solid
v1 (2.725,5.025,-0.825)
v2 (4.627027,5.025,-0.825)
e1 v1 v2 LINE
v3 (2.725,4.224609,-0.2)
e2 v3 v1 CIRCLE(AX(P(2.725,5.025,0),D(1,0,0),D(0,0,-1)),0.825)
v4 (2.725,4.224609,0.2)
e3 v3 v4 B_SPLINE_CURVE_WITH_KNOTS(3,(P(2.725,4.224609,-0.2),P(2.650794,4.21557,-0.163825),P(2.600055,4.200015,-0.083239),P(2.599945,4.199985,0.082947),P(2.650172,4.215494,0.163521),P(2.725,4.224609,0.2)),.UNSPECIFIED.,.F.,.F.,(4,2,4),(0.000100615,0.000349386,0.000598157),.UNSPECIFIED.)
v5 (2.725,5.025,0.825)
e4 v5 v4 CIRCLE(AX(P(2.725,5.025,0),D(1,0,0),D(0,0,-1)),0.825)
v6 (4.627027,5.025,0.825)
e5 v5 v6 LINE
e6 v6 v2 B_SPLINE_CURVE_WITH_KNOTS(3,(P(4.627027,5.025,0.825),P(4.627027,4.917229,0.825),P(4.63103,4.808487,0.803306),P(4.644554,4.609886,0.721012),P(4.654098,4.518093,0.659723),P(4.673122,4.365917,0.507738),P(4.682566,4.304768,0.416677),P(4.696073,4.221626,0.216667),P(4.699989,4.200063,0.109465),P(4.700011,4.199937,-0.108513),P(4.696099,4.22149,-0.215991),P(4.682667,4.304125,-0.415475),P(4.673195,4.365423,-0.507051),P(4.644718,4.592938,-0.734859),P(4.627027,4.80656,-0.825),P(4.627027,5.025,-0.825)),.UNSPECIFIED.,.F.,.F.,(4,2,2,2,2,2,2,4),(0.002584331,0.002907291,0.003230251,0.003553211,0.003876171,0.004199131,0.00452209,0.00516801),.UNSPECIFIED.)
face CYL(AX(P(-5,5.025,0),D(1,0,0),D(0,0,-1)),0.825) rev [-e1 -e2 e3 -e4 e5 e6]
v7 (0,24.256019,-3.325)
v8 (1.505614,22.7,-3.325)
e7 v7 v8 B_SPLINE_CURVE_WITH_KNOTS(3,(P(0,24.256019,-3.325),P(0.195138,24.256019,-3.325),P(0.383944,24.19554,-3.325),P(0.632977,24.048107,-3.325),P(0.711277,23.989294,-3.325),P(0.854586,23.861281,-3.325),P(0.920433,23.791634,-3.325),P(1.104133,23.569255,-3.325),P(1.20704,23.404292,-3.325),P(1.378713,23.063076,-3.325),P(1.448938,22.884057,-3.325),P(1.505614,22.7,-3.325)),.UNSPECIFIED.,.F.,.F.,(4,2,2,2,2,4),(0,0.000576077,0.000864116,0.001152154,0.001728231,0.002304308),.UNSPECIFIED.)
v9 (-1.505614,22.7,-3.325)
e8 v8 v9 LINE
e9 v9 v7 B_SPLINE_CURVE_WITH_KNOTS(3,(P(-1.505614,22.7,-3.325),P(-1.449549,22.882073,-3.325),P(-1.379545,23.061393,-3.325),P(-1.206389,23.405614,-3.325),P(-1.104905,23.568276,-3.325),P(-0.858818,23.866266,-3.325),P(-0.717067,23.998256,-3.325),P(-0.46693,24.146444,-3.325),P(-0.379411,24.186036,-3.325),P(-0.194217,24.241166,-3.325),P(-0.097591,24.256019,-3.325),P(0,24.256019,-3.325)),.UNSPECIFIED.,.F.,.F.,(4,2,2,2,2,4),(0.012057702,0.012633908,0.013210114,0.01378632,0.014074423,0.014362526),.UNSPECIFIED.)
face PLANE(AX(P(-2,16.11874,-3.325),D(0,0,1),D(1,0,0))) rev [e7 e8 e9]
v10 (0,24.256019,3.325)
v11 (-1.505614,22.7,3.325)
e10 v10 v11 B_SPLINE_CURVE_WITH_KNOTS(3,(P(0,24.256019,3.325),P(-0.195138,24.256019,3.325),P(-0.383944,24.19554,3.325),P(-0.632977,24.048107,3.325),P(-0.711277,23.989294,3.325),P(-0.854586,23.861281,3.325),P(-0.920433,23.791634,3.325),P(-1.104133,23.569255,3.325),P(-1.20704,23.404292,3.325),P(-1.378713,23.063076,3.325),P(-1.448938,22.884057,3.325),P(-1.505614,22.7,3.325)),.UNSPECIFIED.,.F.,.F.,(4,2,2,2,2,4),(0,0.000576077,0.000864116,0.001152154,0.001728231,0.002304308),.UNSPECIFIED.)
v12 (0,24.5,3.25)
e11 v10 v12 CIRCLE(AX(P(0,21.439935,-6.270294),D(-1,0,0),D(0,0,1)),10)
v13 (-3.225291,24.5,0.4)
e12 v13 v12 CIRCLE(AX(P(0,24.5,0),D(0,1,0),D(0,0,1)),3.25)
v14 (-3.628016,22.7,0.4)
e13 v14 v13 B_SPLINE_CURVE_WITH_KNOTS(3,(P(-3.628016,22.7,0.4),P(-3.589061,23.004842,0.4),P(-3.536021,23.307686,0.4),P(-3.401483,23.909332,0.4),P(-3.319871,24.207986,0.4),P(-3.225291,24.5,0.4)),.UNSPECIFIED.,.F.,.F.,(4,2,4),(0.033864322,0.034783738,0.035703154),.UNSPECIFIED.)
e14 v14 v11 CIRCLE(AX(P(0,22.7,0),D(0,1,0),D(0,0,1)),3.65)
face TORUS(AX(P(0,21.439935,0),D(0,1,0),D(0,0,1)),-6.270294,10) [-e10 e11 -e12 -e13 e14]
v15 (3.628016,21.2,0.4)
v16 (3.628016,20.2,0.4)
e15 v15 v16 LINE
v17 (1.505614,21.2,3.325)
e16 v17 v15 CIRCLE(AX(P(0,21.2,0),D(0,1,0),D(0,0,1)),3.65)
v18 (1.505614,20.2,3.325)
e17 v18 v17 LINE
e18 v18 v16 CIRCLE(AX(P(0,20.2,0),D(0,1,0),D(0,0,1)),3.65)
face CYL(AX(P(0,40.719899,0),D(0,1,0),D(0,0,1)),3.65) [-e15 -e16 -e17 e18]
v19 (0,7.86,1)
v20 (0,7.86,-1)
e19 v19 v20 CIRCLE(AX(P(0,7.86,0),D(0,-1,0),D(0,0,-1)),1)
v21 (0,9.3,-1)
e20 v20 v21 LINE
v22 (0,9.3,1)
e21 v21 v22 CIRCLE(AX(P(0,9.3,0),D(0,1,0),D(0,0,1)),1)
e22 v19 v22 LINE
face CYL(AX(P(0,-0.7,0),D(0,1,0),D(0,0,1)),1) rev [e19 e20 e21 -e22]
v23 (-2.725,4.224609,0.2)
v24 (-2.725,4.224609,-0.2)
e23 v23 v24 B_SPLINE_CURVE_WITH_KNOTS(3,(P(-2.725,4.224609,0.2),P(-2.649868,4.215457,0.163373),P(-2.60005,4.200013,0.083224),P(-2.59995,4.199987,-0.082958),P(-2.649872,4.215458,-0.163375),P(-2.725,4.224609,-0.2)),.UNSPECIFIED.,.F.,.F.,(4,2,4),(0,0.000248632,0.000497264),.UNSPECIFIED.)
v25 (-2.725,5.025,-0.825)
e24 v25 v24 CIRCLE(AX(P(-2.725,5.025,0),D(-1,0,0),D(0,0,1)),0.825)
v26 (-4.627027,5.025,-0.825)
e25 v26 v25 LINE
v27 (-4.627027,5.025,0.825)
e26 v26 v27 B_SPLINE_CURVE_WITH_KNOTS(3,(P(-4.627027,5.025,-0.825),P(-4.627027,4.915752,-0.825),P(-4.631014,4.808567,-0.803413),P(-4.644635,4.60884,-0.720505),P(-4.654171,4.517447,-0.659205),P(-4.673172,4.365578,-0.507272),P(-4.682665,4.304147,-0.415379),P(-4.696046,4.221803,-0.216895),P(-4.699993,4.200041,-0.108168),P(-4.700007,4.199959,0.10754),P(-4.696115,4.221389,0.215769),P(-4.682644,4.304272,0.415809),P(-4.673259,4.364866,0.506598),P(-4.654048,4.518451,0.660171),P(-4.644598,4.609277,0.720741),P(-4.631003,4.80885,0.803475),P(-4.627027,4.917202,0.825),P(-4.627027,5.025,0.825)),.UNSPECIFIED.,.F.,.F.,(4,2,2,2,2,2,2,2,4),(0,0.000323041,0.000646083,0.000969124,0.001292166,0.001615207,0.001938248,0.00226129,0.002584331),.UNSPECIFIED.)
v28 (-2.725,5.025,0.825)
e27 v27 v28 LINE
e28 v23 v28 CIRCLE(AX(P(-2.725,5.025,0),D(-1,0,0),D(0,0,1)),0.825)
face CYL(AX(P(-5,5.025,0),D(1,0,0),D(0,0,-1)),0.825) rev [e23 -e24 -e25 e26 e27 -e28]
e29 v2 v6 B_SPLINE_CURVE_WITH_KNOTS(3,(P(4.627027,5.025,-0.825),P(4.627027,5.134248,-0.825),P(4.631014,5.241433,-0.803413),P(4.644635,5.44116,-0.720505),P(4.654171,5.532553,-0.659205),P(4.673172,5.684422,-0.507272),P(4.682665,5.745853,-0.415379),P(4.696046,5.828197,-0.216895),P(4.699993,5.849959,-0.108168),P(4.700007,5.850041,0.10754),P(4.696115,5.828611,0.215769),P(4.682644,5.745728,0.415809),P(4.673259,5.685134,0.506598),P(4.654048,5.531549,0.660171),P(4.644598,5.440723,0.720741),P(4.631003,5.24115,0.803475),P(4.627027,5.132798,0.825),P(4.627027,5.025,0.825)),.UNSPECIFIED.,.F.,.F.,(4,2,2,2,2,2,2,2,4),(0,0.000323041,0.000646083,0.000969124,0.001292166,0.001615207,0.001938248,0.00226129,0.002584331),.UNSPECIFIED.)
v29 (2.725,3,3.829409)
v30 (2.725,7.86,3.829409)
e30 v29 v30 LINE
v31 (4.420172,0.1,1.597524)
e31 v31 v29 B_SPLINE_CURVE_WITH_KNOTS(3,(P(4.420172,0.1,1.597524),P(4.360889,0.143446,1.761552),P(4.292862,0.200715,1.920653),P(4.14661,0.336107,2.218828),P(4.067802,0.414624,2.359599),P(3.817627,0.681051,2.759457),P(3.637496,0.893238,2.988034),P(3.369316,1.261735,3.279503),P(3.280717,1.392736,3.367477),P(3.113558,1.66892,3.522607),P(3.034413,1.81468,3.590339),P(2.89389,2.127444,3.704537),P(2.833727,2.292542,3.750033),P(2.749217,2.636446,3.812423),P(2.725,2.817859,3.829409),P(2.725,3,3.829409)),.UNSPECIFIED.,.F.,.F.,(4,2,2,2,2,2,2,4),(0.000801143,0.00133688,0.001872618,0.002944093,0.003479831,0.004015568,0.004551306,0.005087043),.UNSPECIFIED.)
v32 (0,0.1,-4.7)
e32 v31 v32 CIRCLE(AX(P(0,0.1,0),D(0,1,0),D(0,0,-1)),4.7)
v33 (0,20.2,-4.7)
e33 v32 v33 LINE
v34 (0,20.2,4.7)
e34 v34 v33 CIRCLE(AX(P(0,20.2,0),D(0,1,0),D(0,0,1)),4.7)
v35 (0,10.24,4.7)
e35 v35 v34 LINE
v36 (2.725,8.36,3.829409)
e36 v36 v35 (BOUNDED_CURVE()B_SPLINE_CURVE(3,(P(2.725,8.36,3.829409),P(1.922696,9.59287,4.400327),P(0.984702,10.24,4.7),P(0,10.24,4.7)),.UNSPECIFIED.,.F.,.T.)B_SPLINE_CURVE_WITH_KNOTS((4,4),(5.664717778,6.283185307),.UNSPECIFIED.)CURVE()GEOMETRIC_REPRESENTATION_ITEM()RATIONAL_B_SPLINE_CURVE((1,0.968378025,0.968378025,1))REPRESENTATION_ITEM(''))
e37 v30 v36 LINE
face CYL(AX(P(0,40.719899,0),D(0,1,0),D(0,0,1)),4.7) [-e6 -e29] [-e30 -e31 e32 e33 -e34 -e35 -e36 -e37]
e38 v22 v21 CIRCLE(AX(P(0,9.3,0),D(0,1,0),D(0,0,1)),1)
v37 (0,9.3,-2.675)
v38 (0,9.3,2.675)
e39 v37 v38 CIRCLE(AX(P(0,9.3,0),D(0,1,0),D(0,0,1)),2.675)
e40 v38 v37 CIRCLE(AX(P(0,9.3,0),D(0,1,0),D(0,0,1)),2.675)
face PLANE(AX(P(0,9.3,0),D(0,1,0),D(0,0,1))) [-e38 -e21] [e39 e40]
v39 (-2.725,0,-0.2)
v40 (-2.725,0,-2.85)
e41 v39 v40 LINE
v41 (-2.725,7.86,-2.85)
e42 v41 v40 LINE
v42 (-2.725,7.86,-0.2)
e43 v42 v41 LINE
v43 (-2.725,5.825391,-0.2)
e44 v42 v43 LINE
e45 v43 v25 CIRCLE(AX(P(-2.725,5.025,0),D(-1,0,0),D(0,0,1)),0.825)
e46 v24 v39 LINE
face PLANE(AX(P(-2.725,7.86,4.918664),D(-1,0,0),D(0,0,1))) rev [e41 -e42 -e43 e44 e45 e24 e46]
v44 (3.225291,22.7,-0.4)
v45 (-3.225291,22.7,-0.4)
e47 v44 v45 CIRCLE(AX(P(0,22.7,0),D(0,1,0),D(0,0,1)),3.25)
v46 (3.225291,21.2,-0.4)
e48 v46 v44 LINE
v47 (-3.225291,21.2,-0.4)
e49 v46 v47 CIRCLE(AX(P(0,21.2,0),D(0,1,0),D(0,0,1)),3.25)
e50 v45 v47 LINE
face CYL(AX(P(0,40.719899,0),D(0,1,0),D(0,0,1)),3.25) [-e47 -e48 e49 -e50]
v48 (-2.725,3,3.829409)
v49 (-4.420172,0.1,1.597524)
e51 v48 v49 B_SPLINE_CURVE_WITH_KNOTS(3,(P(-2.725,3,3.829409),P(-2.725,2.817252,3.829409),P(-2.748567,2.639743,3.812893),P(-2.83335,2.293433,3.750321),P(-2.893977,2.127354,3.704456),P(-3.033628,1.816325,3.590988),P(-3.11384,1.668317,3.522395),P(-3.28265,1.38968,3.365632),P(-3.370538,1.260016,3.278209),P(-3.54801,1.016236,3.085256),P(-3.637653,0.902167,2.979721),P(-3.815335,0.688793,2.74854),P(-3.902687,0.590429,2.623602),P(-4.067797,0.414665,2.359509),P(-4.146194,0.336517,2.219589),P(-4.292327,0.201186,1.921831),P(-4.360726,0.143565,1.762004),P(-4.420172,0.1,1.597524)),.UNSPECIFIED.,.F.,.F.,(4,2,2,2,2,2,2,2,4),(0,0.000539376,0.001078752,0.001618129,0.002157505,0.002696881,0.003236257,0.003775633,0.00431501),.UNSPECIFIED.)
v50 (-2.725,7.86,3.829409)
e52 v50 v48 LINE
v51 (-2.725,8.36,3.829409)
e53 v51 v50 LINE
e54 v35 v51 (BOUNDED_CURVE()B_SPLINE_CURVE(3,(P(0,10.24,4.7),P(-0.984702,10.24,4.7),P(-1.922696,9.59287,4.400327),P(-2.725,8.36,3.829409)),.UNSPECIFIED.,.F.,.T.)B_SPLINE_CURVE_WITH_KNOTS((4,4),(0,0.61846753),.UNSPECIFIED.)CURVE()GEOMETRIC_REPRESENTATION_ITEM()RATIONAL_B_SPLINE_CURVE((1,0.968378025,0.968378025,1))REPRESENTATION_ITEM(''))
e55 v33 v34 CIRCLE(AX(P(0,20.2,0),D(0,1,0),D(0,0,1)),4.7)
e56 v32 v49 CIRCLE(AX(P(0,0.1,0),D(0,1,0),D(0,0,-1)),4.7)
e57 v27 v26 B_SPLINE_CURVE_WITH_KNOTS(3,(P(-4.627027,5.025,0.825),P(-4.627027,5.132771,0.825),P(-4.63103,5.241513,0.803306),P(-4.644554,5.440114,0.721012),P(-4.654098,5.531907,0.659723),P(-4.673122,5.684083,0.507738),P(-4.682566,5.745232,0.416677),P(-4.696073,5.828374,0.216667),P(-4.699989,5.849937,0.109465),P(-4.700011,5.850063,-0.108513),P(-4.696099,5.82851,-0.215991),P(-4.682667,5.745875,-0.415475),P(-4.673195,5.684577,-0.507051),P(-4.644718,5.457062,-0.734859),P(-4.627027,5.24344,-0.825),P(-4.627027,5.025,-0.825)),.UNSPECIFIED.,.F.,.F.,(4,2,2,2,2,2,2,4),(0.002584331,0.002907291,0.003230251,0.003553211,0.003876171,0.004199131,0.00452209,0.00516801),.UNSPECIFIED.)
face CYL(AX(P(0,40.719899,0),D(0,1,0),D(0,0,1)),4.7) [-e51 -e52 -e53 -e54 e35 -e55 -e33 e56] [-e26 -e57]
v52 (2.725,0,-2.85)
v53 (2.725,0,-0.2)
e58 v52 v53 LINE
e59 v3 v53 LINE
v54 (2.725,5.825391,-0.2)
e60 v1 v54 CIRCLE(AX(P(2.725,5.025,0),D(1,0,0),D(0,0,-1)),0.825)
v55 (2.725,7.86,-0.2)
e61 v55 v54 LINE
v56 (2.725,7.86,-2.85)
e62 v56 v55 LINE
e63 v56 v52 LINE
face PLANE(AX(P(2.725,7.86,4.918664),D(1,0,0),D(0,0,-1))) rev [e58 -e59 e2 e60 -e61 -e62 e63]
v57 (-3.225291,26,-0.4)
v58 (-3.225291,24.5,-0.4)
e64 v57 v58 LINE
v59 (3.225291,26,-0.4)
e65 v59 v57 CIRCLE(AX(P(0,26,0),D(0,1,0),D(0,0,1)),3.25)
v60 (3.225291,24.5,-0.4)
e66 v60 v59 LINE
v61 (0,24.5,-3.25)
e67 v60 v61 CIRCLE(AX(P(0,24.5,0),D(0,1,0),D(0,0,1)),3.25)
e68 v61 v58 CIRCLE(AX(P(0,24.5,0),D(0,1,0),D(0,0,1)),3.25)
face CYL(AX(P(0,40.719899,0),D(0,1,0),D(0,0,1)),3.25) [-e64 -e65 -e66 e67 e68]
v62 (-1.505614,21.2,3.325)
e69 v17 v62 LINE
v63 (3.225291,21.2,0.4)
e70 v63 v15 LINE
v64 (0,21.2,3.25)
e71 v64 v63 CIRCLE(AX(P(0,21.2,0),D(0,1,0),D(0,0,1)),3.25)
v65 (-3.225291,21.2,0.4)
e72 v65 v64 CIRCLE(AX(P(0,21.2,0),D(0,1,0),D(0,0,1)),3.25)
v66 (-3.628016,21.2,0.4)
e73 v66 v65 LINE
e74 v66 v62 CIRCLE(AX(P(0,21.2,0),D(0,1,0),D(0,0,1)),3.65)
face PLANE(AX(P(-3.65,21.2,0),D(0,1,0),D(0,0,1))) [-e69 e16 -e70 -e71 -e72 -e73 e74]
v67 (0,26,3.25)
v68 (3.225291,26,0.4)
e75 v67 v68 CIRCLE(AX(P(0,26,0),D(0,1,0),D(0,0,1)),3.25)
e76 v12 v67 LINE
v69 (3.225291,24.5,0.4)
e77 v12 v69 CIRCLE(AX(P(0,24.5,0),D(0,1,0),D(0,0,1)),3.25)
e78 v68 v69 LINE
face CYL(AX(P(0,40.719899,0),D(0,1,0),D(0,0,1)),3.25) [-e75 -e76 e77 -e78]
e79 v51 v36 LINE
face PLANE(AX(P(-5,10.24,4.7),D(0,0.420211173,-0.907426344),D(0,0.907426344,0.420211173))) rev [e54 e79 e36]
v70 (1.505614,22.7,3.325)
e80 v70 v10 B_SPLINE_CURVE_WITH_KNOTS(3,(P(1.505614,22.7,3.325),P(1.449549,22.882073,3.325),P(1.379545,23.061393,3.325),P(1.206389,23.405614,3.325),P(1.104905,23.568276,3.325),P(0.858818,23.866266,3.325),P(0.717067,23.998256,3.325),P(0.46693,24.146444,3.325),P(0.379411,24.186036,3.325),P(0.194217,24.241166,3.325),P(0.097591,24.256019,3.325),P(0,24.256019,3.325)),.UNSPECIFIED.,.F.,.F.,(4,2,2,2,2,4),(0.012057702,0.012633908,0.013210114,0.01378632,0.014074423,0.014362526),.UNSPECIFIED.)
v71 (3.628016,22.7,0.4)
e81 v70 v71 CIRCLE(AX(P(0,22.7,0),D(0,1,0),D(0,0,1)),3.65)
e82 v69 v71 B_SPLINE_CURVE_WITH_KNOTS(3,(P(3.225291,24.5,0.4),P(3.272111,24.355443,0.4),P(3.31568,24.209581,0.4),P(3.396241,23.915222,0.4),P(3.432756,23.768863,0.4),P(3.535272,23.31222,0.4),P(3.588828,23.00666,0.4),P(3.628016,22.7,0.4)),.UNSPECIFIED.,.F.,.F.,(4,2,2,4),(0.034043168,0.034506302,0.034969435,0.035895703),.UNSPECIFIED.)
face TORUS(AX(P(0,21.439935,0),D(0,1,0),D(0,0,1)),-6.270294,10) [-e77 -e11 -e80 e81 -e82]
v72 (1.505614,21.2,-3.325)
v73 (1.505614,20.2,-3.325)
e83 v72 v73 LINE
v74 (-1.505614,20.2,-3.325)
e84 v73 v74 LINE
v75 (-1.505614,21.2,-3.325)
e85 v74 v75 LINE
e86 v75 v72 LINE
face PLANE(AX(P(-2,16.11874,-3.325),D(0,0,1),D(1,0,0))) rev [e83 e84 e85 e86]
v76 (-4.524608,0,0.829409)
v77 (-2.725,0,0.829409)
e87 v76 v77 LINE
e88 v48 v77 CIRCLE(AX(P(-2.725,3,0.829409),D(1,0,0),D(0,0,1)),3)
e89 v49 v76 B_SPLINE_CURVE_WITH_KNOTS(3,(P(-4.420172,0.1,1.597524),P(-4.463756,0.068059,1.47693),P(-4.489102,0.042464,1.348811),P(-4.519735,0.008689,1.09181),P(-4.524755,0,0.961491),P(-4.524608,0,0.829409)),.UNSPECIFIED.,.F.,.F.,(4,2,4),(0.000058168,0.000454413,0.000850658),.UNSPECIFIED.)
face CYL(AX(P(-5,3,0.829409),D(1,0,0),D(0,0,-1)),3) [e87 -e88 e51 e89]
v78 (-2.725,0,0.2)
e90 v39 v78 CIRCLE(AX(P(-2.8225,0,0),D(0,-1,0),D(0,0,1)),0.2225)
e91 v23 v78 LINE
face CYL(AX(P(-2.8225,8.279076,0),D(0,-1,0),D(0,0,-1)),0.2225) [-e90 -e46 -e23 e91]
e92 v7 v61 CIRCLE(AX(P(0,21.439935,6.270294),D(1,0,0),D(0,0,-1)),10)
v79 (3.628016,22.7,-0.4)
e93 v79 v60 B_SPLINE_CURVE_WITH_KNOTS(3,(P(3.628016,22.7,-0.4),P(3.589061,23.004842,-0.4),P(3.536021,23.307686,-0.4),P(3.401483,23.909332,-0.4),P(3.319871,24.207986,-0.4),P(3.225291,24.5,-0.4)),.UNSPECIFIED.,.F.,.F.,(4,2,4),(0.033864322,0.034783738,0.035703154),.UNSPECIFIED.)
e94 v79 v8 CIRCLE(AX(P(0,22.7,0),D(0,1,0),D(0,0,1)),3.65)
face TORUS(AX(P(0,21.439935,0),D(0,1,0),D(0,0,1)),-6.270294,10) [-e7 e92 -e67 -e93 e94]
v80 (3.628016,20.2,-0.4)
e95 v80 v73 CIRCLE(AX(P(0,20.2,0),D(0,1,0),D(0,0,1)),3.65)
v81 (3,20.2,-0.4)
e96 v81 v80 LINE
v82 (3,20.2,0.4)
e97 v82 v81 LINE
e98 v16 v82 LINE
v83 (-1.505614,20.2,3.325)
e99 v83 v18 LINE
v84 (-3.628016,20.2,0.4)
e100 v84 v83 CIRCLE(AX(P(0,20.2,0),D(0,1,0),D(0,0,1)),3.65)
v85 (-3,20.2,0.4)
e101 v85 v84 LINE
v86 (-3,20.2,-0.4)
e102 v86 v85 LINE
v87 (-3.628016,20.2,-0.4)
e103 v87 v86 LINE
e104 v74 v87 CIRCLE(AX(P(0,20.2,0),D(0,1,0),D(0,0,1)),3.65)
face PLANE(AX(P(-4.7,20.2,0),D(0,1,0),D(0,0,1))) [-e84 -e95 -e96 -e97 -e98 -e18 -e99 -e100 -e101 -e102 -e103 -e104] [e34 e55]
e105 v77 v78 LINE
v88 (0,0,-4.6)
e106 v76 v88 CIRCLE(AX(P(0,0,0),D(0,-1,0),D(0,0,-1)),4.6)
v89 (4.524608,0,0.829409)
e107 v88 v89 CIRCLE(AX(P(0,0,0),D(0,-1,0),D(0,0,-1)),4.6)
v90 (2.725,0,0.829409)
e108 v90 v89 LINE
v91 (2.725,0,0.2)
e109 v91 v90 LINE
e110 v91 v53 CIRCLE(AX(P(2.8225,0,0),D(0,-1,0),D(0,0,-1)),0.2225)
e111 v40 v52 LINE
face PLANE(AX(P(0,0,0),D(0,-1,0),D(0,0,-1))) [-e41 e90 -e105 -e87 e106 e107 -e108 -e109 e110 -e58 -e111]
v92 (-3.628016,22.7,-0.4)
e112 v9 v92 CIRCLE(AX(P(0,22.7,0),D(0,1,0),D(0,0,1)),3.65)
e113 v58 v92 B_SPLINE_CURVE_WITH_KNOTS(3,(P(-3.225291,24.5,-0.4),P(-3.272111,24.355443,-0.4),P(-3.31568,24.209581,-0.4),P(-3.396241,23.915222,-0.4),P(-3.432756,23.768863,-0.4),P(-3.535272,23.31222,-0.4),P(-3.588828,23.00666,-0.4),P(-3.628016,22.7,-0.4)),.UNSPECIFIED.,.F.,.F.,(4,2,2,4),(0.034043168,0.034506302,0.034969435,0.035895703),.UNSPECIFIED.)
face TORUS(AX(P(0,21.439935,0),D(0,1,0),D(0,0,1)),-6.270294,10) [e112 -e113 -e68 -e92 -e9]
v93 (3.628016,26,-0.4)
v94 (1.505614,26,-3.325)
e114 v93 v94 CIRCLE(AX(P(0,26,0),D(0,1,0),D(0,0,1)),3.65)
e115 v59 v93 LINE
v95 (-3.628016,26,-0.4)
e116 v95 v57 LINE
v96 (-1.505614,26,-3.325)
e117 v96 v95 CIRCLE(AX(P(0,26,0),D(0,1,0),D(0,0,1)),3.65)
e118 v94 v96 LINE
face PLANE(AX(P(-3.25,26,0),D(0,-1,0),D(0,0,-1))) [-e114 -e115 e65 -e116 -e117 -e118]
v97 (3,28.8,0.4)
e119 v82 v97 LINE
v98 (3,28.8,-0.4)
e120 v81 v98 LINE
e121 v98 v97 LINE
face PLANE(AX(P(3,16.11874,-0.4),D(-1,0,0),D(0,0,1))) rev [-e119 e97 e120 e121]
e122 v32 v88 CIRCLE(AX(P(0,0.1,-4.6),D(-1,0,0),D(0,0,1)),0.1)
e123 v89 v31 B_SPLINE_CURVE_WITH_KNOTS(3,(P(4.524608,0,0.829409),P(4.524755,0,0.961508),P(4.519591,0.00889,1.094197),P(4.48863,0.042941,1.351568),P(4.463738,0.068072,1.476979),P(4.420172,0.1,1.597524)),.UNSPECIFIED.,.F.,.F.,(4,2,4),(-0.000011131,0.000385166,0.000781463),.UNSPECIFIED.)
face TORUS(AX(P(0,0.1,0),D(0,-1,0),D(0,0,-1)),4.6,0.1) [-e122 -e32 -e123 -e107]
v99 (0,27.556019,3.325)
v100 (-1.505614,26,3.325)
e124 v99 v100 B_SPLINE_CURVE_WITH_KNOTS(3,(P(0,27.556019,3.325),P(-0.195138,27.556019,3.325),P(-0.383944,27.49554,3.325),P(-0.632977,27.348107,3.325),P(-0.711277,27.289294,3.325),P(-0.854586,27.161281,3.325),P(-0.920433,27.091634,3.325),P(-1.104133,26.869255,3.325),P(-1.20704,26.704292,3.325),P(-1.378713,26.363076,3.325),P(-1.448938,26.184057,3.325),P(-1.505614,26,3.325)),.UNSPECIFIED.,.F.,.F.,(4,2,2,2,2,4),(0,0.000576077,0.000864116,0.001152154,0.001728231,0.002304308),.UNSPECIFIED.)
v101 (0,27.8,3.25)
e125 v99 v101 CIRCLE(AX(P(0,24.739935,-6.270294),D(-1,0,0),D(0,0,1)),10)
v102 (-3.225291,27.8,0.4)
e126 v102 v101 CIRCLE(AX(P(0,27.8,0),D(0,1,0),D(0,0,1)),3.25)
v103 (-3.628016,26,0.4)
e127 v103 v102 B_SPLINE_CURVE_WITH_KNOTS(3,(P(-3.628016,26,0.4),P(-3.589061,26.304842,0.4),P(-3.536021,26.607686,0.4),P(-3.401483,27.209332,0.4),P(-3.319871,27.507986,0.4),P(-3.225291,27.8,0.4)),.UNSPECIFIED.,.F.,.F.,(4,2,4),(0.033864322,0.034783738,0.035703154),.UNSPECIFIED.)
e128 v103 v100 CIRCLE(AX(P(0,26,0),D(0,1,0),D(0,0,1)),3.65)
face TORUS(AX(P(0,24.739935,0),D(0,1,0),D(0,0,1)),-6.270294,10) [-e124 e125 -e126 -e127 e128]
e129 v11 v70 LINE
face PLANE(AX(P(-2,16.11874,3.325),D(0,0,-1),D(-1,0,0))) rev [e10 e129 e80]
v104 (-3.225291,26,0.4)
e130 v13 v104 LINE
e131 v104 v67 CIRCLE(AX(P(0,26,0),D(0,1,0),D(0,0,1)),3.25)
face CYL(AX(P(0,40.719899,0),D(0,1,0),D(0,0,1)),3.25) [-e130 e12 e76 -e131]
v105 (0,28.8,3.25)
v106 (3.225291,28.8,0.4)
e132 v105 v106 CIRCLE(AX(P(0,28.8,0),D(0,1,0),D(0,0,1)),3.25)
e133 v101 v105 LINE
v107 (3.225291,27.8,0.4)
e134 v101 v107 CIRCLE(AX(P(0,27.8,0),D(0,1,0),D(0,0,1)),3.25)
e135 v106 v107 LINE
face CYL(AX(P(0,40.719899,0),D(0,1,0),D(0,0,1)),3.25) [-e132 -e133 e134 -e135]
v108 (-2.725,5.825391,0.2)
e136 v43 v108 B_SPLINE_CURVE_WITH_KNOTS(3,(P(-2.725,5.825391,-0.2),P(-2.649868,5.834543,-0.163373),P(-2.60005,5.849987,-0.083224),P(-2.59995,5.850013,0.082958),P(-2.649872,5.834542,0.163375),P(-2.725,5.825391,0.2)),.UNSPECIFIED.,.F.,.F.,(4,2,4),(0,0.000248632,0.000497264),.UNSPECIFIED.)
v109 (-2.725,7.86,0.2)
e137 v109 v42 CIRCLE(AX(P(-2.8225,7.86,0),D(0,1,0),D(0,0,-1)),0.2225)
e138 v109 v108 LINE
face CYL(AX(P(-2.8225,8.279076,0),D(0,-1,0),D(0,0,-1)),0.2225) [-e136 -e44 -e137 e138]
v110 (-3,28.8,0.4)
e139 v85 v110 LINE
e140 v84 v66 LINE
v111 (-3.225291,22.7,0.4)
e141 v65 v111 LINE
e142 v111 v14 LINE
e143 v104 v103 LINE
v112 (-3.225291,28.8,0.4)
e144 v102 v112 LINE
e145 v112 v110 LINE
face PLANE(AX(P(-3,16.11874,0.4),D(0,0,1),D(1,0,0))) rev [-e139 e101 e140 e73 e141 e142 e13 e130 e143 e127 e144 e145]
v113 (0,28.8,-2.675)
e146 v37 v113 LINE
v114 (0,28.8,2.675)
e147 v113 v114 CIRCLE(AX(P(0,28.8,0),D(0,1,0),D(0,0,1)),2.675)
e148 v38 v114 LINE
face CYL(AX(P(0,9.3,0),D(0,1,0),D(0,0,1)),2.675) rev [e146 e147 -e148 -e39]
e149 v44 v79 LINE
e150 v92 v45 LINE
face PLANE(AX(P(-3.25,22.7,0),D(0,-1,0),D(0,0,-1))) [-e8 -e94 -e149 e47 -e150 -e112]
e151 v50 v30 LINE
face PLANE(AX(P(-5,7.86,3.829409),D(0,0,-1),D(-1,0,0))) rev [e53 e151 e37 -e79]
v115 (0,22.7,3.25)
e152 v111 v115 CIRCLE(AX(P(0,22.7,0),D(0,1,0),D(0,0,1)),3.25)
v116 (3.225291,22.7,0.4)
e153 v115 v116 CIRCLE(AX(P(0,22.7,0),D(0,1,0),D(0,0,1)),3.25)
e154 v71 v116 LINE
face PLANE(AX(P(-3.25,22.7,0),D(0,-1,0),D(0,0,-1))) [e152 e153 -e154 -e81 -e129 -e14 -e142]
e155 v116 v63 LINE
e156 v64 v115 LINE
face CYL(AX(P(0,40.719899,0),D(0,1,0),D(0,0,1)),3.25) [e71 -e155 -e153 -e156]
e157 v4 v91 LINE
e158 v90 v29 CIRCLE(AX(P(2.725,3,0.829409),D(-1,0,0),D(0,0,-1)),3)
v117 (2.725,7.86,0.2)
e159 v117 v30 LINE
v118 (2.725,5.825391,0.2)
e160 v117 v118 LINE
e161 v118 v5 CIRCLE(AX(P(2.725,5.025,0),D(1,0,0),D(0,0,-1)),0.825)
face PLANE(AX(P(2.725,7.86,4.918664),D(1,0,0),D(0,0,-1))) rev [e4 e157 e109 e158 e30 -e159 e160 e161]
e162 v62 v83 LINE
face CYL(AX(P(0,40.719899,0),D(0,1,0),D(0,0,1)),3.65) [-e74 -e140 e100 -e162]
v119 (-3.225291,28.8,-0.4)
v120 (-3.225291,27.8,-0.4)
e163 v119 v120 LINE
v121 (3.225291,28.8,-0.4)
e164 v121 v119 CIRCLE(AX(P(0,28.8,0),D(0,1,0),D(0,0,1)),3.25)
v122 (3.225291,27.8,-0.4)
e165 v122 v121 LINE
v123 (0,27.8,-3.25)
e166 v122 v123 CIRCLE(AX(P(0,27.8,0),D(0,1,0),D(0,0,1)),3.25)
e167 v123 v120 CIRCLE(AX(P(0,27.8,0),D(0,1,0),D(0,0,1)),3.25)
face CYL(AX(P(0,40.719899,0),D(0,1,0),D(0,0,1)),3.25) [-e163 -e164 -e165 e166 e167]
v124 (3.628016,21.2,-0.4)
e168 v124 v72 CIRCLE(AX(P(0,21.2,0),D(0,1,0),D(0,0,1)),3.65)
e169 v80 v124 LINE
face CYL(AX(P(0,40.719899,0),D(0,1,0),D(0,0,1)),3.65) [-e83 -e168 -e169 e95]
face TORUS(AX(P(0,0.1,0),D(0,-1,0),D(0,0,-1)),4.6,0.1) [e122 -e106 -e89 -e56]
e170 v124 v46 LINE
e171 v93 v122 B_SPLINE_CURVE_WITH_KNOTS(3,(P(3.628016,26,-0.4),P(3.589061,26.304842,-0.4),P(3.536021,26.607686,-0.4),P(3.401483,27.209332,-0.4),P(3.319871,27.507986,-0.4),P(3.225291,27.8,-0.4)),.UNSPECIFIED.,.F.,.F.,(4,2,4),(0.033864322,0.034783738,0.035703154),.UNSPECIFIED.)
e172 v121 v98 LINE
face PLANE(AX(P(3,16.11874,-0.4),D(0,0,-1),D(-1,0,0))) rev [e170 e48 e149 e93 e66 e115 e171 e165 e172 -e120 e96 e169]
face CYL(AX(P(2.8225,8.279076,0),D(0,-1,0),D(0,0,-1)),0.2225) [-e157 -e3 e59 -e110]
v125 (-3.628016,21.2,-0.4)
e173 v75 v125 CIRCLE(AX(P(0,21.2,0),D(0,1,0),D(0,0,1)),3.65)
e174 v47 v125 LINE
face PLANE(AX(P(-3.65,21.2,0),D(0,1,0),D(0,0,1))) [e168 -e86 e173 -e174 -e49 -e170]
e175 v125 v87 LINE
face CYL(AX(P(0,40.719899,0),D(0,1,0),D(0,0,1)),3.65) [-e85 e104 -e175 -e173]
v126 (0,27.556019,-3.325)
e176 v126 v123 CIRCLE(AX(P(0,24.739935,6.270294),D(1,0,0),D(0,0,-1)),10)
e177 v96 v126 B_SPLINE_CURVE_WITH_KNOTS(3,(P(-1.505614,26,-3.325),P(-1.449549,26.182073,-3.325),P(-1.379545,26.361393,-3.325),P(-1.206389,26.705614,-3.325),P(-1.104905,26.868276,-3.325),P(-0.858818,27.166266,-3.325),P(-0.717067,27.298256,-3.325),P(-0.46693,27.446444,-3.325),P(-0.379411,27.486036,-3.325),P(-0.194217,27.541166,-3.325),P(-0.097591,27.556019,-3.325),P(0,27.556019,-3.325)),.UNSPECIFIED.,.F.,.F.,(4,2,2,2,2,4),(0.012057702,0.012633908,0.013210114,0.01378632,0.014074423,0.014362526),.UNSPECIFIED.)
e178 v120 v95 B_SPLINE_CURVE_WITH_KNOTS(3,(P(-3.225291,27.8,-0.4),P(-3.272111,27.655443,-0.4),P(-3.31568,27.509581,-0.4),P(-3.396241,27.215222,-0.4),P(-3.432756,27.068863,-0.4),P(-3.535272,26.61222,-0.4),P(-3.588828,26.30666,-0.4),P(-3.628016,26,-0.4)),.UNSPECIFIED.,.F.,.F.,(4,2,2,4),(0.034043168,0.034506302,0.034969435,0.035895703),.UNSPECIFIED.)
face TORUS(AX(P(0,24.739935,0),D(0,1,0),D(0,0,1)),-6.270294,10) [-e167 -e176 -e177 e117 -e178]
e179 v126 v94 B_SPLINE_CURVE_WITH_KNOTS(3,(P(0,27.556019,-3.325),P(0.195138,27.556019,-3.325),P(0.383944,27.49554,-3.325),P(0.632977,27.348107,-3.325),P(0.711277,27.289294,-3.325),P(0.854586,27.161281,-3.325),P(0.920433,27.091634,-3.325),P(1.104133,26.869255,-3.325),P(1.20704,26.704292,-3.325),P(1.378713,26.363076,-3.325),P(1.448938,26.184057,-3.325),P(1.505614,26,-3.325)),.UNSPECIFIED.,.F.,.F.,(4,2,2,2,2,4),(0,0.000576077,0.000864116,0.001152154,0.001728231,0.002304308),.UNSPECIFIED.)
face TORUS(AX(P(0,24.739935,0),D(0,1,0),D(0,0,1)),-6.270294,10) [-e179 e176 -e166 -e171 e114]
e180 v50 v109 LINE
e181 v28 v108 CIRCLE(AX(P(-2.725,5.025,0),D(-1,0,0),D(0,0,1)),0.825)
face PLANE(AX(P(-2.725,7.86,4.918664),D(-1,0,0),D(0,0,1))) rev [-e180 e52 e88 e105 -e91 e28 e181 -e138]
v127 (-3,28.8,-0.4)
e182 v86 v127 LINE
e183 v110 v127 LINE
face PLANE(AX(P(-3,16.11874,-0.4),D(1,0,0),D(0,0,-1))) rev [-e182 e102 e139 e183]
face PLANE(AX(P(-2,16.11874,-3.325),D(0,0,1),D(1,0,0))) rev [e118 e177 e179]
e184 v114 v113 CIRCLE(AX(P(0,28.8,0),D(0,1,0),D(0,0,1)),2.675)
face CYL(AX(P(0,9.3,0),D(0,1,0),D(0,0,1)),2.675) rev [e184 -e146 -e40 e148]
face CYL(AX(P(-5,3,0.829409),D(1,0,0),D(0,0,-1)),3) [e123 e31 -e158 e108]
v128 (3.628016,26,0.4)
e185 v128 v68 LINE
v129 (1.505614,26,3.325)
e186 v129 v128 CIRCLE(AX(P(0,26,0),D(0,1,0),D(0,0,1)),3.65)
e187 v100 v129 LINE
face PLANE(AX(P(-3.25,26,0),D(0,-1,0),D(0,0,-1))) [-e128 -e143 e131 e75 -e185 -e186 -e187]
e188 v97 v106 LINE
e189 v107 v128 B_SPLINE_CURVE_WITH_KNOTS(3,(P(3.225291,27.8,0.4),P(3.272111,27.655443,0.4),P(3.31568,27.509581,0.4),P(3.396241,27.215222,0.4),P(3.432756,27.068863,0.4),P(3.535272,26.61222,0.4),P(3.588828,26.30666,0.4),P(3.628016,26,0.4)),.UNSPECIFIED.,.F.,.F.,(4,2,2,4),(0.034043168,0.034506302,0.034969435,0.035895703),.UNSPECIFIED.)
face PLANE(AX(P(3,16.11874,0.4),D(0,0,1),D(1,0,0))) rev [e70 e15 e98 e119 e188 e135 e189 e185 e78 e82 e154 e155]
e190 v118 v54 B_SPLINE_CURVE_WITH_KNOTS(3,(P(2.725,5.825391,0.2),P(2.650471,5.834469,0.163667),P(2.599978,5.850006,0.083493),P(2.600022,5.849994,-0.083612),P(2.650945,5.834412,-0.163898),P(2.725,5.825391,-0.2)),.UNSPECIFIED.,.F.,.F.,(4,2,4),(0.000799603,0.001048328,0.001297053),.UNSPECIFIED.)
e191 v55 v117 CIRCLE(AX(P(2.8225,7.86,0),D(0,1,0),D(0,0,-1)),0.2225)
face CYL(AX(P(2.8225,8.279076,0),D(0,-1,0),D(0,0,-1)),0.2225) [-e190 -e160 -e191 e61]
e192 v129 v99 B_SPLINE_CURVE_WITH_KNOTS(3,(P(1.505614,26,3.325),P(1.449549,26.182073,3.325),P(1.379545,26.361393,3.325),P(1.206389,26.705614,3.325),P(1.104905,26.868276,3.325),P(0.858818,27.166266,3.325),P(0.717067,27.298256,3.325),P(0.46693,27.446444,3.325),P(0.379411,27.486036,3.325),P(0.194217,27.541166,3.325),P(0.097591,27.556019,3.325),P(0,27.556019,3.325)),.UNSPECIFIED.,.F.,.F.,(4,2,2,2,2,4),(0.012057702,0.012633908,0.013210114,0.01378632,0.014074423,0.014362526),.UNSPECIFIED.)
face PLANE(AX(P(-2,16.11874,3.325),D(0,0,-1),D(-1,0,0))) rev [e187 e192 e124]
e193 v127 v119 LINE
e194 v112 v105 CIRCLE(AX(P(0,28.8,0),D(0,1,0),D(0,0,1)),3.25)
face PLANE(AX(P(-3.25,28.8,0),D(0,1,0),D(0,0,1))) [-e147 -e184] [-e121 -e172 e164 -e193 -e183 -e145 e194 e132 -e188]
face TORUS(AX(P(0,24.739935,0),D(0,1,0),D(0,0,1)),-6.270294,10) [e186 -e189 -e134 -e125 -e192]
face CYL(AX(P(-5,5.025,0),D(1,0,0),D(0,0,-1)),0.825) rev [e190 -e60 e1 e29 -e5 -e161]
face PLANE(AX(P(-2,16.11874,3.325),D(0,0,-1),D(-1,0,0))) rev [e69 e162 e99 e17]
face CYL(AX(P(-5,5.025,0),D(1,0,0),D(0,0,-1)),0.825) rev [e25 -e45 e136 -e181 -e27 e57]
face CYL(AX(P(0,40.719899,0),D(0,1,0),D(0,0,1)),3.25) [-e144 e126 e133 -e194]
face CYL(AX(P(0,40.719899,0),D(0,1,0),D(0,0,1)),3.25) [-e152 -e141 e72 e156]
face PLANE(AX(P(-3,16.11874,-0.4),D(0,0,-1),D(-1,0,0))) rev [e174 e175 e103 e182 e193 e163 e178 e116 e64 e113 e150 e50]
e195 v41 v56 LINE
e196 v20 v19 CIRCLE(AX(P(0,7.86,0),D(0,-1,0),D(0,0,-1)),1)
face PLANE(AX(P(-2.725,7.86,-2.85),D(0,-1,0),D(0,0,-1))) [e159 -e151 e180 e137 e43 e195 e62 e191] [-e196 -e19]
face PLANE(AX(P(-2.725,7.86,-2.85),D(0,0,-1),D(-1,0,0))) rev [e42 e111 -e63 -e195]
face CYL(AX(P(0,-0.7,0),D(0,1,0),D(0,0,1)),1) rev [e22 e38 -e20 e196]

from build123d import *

# Parameters (mm, degrees)
SKETCH_3_R          = 2.675
CUT_EXTRUDE_1_DEPTH = 19.5
SKETCH_4_W          = 5.45
SKETCH_4_H          = 7.768663762
CUT_EXTRUDE_2_DEPTH = 7.86
CUT_EXTRUDE_4_REACH = 31.557
SKETCH_6_W          = 1.34037146
SKETCH_6_H          = 0.8
SKETCH_6_W_2        = 4
SKETCH_6_H_2        = 0.810357856
FILLET_8_R          = 0.1
SKETCH_7_R          = 1
CUT_EXTRUDE_5_DEPTH = 10
EXTRUDE_1_DEPTH     = 7.86
SKETCH_5_R          = 0.825
CUT_EXTRUDE_3_DEPTH = 5


with BuildPart() as part:
    # 草图1 → 旋转1 (revolve)
    with BuildSketch(Plane.XY, mode=Mode.PRIVATE) as revolve_1_sk:
        with BuildLine():
            Line((0, 0), (-4.7, 0))
            Line((-4.7, 0), (-4.7, 20.2))
            Line((-4.7, 20.2), (-3.65, 20.2))
            Line((-3.65, 20.2), (-3.65, 21.2))
            Line((-3.65, 21.2), (-3.25, 21.2))
            Line((-3.25, 21.2), (-3.25, 22.7))
            Line((-3.25, 22.7), (-3.65, 22.7))
            ThreePointArc((-3.65, 22.7), (-3.491576489, 23.60923922), (-3.25, 24.5))
            Line((-3.25, 24.5), (-3.25, 26))
            Line((-3.25, 26), (-3.65, 26))
            ThreePointArc((-3.65, 26), (-3.491576489, 26.90923922), (-3.25, 27.8))
            Line((-3.25, 27.8), (-3.25, 28.8))
            Line((-3.25, 28.8), (0, 28.8))
            Line((0, 28.8), (0, 0))
        make_face()
    revolve(revolve_1_sk.sketch.rotate(Axis((0, 40.719898965, 0), (0, -1, 0)), 270), axis=Axis((0, 40.719898965, 0), (0, -1, 0)))

    # 草图3 → 切除-拉伸1 (cut)
    with BuildSketch(Plane(origin=(0, 28.8, 0), x_dir=(1, 0, 0), z_dir=(0, 1, 0))):
        with Locations(Location((0, 0, 0), (0, 0, 270))):
            Circle(SKETCH_3_R)
    extrude(amount=-CUT_EXTRUDE_1_DEPTH, mode=Mode.SUBTRACT)

    # 草图4 → 切除-拉伸2 (cut)
    with BuildSketch(Plane.XZ):
        with Locations((0, 1.034331881)):
            Rectangle(SKETCH_4_W, SKETCH_4_H)
    extrude(amount=-CUT_EXTRUDE_2_DEPTH, mode=Mode.SUBTRACT)

    # 切除-拉伸4: up to this face of the body (flat: up to its plane)
    cut_extrude_4_end = Plane(part.part.faces().sort_by_distance((0, 20.2, -4.567063925))[0])
    # 草图6 → 切除-拉伸4 (cut, up to the picked face)
    with BuildSketch(Plane(origin=(0, 28.8, 0), x_dir=(1, 0, 0), z_dir=(0, 1, 0)), mode=Mode.PRIVATE) as cut_extrude_4_sk1:
        with Locations((-3.67018573, 0)):
            Rectangle(SKETCH_6_W, SKETCH_6_H)
    cut_extrude_4_tool1 = split(extrude(cut_extrude_4_sk1.sketch, amount=-CUT_EXTRUDE_4_REACH, mode=Mode.PRIVATE), bisect_by=cut_extrude_4_end, keep=Keep.BOTH, mode=Mode.PRIVATE)
    # 草图6 → 切除-拉伸4 (cut, up to the picked face)
    with BuildSketch(Plane(origin=(0, 28.8, 0), x_dir=(1, 0, 0), z_dir=(0, 1, 0)), mode=Mode.PRIVATE) as cut_extrude_4_sk2:
        with Locations((3.67018573, 0)):
            Rectangle(SKETCH_6_W, SKETCH_6_H)
    cut_extrude_4_tool2 = split(extrude(cut_extrude_4_sk2.sketch, amount=-CUT_EXTRUDE_4_REACH, mode=Mode.PRIVATE), bisect_by=cut_extrude_4_end, keep=Keep.BOTH, mode=Mode.PRIVATE)
    # 草图6 → 切除-拉伸4 (cut, up to the picked face)
    with BuildSketch(Plane(origin=(0, 28.8, 0), x_dir=(1, 0, 0), z_dir=(0, 1, 0)), mode=Mode.PRIVATE) as cut_extrude_4_sk3:
        with Locations((0, -3.730178928)):
            Rectangle(SKETCH_6_W_2, SKETCH_6_H_2)
    cut_extrude_4_tool3 = split(extrude(cut_extrude_4_sk3.sketch, amount=-CUT_EXTRUDE_4_REACH, mode=Mode.PRIVATE), bisect_by=cut_extrude_4_end, keep=Keep.BOTH, mode=Mode.PRIVATE)
    # 草图6 → 切除-拉伸4 (cut, up to the picked face)
    with BuildSketch(Plane(origin=(0, 28.8, 0), x_dir=(1, 0, 0), z_dir=(0, 1, 0)), mode=Mode.PRIVATE) as cut_extrude_4_sk4:
        with Locations((0, 3.730178928)):
            Rectangle(SKETCH_6_W_2, SKETCH_6_H_2)
    cut_extrude_4_tool4 = split(extrude(cut_extrude_4_sk4.sketch, amount=-CUT_EXTRUDE_4_REACH, mode=Mode.PRIVATE), bisect_by=cut_extrude_4_end, keep=Keep.BOTH, mode=Mode.PRIVATE)
    add(cut_extrude_4_tool1.solids().sort_by(Axis((-3.670186, 28.8, 0), (0, -1, 0)))[0], mode=Mode.SUBTRACT)
    add(cut_extrude_4_tool2.solids().sort_by(Axis((3.670186, 28.8, 0), (0, -1, 0)))[0], mode=Mode.SUBTRACT)
    add(cut_extrude_4_tool3.solids().sort_by(Axis((0, 28.8, 3.730179), (0, -1, 0)))[0], mode=Mode.SUBTRACT)
    add(cut_extrude_4_tool4.solids().sort_by(Axis((0, 28.8, -3.730179), (0, -1, 0)))[0], mode=Mode.SUBTRACT)

    # 圆角8
    fillet_8_edges = [part.edges().sort_by_distance(p)[0] for p in [
        (0, 0, -4.7),
    ]]
    fillet(fillet_8_edges, radius=FILLET_8_R)

    # 草图7 → 切除-拉伸5 (cut)
    with BuildSketch(Plane(origin=(0, 9.3, 0), x_dir=(1, 0, 0), z_dir=(0, 1, 0))):
        with Locations(Location((0, 0, 0), (0, 0, 270))):
            Circle(SKETCH_7_R)
    extrude(amount=-CUT_EXTRUDE_5_DEPTH, mode=Mode.SUBTRACT)

    # 草图8 → 凸台-拉伸1 (add)
    with BuildSketch(Plane.XZ):
        with BuildLine():
            Line((2.725, -0.2), (2.725, 0.2))
            ThreePointArc((2.725, 0.2), (2.6, 0), (2.725, -0.2))
        make_face()
        with BuildLine():
            Line((-2.725, -0.2), (-2.725, 0.2))
            ThreePointArc((-2.725, 0.2), (-2.6, 0), (-2.725, -0.2))
        make_face()
    extrude(amount=-EXTRUDE_1_DEPTH)

    # 草图5 → 切除-拉伸3 (cut, symmetric)
    with BuildSketch(Plane(origin=(0, 0, 0), x_dir=(0, 0, -1), z_dir=(1, 0, 0))):
        with Locations((0, 5.025)):
            Circle(SKETCH_5_R)
        Polygon((-4.7, 10.24), (-3.829409223, 8.36), (-3.829409223, 7.86), (-3.829409223, 3.115780314), (-4.7, 3.115780314), align=None)
        with BuildLine():
            Line((-3.829409223, 3), (-4.605698774, 3))
            Line((-4.605698774, 3), (-4.605698774, 0))
            Line((-4.605698774, 0), (-0.829409223, 0))
            ThreePointArc((-0.829409223, 0), (-2.950729567, 0.878679656), (-3.829409223, 3))
        make_face()
    extrude(amount=CUT_EXTRUDE_3_DEPTH, both=True, mode=Mode.SUBTRACT)


solid = part.part
